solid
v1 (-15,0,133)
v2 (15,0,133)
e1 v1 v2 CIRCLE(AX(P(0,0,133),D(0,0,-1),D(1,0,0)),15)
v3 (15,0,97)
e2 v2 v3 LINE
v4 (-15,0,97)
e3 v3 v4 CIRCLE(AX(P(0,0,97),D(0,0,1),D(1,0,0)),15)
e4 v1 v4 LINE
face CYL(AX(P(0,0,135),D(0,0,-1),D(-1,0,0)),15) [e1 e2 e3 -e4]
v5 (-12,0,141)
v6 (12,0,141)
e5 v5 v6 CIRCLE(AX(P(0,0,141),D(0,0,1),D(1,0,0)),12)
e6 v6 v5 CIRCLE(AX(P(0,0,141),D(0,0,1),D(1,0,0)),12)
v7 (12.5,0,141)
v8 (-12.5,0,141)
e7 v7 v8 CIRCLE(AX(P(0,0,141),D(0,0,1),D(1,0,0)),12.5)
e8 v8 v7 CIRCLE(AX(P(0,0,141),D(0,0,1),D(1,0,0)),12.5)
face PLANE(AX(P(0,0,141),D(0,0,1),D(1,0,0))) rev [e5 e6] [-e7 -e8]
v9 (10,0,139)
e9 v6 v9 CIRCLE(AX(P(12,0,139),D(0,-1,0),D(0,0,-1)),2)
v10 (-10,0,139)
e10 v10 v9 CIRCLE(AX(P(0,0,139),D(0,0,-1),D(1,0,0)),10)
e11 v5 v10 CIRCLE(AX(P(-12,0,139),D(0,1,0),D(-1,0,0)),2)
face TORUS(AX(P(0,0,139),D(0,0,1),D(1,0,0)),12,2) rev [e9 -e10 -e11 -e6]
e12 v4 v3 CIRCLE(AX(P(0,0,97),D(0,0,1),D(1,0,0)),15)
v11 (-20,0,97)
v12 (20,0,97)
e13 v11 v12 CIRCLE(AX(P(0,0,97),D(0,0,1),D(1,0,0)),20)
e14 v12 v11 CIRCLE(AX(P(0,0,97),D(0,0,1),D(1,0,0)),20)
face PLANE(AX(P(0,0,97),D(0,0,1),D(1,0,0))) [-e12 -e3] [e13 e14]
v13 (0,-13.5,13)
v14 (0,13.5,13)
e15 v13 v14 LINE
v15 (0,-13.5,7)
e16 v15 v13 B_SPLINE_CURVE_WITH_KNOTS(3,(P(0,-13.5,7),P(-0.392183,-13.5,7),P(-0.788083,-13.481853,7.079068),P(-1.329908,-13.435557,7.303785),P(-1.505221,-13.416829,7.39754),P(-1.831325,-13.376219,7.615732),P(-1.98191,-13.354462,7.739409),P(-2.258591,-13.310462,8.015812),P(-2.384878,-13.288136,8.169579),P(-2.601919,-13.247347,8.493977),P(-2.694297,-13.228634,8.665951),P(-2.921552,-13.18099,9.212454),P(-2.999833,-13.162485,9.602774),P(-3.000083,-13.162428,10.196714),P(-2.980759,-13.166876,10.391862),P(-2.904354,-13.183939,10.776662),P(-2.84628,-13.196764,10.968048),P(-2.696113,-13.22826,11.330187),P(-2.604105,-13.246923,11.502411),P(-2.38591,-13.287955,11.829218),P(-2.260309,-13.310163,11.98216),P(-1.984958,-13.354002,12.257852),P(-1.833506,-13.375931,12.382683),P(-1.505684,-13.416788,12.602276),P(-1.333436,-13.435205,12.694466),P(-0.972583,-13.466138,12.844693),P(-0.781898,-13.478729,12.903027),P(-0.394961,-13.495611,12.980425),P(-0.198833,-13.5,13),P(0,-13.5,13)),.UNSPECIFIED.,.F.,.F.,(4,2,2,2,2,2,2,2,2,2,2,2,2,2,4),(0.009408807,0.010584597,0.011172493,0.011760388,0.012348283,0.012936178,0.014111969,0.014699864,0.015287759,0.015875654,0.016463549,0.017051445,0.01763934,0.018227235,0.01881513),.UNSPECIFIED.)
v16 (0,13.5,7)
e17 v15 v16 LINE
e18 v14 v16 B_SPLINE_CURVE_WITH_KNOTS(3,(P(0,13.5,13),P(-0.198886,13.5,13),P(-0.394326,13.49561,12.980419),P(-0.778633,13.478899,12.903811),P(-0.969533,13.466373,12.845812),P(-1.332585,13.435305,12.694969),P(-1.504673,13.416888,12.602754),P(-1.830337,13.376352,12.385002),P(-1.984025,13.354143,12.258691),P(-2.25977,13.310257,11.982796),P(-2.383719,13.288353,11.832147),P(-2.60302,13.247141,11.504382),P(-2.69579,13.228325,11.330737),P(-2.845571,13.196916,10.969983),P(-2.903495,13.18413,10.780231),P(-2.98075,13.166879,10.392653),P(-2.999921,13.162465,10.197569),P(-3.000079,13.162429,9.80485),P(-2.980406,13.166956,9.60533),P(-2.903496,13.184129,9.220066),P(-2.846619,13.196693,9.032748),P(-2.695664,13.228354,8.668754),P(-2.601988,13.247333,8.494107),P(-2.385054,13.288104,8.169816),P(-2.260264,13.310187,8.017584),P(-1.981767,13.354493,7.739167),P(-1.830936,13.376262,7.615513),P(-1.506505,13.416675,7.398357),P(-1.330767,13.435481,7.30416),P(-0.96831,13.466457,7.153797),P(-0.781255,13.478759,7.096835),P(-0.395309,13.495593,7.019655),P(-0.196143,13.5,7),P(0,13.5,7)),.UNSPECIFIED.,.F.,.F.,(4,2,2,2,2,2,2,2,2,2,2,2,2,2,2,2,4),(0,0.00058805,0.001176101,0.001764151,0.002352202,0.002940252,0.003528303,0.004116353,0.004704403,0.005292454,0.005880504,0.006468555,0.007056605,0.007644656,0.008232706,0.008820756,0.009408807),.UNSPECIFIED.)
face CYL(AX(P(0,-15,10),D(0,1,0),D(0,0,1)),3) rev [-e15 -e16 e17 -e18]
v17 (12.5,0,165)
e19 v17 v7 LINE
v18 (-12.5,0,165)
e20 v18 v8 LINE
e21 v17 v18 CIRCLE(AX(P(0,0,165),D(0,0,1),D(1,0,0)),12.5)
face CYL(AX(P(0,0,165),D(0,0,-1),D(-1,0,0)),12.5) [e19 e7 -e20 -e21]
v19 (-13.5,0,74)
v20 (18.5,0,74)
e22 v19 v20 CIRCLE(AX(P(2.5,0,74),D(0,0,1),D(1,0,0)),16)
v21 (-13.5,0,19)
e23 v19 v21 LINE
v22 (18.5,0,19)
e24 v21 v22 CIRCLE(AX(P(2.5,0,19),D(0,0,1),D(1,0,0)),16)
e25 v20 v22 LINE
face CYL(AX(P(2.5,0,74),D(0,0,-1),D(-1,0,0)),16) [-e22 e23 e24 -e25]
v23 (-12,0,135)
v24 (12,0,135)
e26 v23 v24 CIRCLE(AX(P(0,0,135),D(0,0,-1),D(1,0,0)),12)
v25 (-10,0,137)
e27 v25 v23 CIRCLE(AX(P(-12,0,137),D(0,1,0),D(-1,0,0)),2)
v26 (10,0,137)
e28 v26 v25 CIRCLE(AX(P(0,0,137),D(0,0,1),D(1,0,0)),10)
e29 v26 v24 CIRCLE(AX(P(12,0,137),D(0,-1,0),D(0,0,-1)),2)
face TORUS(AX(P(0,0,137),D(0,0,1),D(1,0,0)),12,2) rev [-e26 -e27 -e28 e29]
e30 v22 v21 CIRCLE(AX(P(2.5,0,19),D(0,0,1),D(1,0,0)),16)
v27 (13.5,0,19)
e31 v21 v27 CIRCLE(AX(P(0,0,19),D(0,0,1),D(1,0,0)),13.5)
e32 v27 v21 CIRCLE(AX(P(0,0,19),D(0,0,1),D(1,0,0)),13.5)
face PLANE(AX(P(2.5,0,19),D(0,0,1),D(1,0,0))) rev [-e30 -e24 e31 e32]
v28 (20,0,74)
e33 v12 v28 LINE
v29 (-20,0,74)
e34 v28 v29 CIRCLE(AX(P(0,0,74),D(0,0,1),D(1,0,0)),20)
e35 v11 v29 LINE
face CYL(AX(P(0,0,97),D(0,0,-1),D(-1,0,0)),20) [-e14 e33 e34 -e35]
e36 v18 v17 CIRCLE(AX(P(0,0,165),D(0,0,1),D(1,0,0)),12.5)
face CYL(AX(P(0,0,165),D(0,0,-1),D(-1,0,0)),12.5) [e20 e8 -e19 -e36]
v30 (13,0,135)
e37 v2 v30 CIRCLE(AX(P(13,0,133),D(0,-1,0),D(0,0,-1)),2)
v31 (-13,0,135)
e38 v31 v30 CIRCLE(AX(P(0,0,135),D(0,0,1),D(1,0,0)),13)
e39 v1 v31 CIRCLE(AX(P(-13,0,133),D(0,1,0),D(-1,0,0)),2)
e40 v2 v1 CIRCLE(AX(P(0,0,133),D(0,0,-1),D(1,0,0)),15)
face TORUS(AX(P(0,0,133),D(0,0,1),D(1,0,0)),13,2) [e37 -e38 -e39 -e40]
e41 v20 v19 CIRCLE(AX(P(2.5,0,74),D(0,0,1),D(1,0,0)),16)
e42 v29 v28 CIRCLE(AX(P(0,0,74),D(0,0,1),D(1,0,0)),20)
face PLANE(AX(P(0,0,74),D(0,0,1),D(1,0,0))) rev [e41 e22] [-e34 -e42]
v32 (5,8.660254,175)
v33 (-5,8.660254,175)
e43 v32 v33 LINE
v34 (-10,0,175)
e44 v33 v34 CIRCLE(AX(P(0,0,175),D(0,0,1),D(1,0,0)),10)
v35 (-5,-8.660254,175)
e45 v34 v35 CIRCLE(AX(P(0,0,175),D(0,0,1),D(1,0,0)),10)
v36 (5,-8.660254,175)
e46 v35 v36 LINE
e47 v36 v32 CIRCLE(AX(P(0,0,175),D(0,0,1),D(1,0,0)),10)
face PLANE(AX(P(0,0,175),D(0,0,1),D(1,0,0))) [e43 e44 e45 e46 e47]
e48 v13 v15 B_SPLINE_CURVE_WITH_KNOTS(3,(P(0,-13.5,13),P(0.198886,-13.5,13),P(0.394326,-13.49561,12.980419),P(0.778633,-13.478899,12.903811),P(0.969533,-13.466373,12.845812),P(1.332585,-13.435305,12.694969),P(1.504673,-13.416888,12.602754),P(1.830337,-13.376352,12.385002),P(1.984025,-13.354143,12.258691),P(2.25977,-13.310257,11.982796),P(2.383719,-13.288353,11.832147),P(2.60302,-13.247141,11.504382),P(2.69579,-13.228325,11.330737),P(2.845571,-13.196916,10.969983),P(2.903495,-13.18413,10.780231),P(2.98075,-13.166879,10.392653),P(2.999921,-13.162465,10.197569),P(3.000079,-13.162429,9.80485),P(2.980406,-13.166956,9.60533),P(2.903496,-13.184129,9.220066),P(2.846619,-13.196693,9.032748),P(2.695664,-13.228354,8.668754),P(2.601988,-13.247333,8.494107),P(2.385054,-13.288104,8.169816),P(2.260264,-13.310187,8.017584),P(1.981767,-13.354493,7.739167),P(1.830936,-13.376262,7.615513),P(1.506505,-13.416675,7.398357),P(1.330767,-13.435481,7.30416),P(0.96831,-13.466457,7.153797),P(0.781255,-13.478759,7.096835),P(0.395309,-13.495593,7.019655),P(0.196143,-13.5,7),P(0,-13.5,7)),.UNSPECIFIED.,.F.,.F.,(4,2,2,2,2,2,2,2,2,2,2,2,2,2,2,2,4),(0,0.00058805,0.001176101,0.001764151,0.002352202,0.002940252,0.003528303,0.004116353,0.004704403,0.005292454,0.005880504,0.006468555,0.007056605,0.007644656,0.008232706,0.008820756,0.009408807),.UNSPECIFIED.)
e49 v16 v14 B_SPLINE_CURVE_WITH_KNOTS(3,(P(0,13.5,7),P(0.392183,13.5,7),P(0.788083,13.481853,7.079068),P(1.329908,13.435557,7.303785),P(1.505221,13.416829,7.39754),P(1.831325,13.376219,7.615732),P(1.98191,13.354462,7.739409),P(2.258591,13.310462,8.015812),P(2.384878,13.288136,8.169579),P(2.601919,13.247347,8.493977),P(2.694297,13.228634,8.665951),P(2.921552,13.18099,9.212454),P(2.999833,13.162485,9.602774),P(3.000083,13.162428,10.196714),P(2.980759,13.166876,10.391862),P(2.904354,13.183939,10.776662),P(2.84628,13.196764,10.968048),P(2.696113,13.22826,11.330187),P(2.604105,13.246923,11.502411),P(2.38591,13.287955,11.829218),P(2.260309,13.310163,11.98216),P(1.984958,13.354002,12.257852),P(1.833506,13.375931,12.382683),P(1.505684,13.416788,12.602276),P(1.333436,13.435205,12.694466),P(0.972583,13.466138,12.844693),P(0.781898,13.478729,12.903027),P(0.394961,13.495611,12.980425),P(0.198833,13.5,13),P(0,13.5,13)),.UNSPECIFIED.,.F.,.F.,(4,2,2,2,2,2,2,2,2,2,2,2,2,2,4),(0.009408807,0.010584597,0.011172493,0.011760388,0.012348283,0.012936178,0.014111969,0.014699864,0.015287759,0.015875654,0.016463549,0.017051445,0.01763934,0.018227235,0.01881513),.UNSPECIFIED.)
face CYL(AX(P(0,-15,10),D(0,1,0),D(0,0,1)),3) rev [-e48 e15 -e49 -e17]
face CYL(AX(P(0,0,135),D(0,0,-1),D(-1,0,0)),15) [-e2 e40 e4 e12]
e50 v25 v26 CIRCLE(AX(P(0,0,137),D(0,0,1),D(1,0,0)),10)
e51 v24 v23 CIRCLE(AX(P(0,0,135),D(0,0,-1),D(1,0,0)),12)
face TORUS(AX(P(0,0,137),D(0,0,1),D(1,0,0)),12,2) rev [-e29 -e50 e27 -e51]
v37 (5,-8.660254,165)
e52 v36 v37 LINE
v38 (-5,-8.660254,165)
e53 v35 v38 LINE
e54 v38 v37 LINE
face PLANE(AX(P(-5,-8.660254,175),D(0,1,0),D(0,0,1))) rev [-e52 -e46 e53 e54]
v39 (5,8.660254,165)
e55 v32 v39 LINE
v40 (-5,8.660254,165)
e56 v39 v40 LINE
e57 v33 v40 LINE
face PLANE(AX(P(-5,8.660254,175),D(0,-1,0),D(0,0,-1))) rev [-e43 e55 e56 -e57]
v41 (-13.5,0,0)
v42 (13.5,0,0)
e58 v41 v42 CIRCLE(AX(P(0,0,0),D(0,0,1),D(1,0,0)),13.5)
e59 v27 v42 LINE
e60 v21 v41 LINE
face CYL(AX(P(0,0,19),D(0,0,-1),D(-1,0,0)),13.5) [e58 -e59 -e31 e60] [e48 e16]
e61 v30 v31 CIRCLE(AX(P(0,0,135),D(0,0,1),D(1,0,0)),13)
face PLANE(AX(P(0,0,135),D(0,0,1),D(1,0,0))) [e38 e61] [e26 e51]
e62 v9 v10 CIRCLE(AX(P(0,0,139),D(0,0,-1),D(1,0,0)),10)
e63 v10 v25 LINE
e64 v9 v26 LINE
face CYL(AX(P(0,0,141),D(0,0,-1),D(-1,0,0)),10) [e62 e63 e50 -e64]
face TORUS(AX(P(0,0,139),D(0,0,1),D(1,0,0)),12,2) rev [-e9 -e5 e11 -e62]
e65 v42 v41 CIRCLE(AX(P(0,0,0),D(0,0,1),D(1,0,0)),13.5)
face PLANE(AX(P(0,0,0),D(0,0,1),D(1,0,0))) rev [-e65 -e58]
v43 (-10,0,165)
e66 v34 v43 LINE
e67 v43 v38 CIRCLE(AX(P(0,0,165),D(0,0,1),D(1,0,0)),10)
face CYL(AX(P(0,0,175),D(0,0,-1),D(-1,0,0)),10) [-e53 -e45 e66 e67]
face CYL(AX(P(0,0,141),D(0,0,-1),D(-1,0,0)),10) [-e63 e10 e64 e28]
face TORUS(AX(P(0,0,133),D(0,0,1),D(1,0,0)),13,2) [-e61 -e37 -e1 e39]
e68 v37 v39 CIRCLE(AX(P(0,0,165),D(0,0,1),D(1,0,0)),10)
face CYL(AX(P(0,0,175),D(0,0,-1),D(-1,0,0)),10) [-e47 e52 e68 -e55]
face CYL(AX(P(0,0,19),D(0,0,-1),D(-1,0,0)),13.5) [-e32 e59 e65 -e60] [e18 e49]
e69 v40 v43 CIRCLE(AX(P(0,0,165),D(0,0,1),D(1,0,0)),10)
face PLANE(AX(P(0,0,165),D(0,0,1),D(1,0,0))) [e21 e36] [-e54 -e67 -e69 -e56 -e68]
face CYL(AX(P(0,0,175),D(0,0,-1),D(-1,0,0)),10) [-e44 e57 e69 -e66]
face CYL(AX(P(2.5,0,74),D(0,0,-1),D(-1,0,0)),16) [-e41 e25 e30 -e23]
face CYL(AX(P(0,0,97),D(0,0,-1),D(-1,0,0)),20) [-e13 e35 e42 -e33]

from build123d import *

# Parameters (mm, degrees)
SKETCH2_R          = 13.5
EXTRUDE1_DEPTH     = 19
SKETCH3_R          = 16
EXTRUDE2_DEPTH     = 55
SKETCH4_R          = 20
EXTRUDE3_DEPTH     = 23
SKETCH5_R          = 15
EXTRUDE4_DEPTH     = 38
SKETCH6_R          = 10
EXTRUDE5_DEPTH     = 6
SKETCH7_R          = 12.5
EXTRUDE6_DEPTH     = 24
EXTRUDE7_DEPTH     = 10
SKETCH9_R          = 3
CUT_EXTRUDE1_DEPTH = 15
FILLET1_R          = 2


with BuildPart() as part:
    # Sketch2 → Extrude1 (new body)
    with BuildSketch(Plane.XY):
        Circle(SKETCH2_R)
    extrude(amount=EXTRUDE1_DEPTH)

    # Sketch3 → Extrude2 (add)
    with BuildSketch(Plane.XY.offset(19)):
        with Locations(Location((2.5, 0, 0), (0, 0, 179.999529266))):
            Circle(SKETCH3_R)
    extrude(amount=EXTRUDE2_DEPTH)

    # Sketch4 → Extrude3 (add)
    with BuildSketch(Plane.XY.offset(74)):
        Circle(SKETCH4_R)
    extrude(amount=EXTRUDE3_DEPTH)

    # Sketch5 → Extrude4 (add)
    with BuildSketch(Plane.XY.offset(97)):
        Circle(SKETCH5_R)
    extrude(amount=EXTRUDE4_DEPTH)

    # Sketch6 → Extrude5 (add)
    with BuildSketch(Plane.XY.offset(135)):
        Circle(SKETCH6_R)
    extrude(amount=EXTRUDE5_DEPTH)

    # Sketch7 → Extrude6 (add)
    with BuildSketch(Plane.XY.offset(141)):
        Circle(SKETCH7_R)
    extrude(amount=EXTRUDE6_DEPTH)

    # Sketch8 → Extrude7 (add)
    with BuildSketch(Plane.XY.offset(165)):
        with BuildLine():
            Line((-5, 8.660254038), (5, 8.660254038))
            ThreePointArc((5, 8.660254038), (10, 0), (5, -8.660254038))
            Line((5, -8.660254038), (-5, -8.660254038))
            ThreePointArc((-5, -8.660254038), (-10, 0), (-5, 8.660254038))
        make_face()
    extrude(amount=EXTRUDE7_DEPTH)

    # Sketch9 → Cut-Extrude1 (cut, symmetric)
    with BuildSketch(Plane(origin=(0, 0, 0), x_dir=(1, 0, 0), z_dir=(0, 1, 0))):
        with Locations(Location((0, -10, 0), (0, 0, 270))):
            Circle(SKETCH9_R)
    extrude(amount=CUT_EXTRUDE1_DEPTH, both=True, mode=Mode.SUBTRACT)

    # Fillet1
    fillet1_edges = [part.edges().sort_by_distance(p)[0] for p in [
        (-15, 0, 135),
        (-10, 0, 135),
        (-10, 0, 141),
    ]]
    fillet(fillet1_edges, radius=FILLET1_R)


solid = part.part
